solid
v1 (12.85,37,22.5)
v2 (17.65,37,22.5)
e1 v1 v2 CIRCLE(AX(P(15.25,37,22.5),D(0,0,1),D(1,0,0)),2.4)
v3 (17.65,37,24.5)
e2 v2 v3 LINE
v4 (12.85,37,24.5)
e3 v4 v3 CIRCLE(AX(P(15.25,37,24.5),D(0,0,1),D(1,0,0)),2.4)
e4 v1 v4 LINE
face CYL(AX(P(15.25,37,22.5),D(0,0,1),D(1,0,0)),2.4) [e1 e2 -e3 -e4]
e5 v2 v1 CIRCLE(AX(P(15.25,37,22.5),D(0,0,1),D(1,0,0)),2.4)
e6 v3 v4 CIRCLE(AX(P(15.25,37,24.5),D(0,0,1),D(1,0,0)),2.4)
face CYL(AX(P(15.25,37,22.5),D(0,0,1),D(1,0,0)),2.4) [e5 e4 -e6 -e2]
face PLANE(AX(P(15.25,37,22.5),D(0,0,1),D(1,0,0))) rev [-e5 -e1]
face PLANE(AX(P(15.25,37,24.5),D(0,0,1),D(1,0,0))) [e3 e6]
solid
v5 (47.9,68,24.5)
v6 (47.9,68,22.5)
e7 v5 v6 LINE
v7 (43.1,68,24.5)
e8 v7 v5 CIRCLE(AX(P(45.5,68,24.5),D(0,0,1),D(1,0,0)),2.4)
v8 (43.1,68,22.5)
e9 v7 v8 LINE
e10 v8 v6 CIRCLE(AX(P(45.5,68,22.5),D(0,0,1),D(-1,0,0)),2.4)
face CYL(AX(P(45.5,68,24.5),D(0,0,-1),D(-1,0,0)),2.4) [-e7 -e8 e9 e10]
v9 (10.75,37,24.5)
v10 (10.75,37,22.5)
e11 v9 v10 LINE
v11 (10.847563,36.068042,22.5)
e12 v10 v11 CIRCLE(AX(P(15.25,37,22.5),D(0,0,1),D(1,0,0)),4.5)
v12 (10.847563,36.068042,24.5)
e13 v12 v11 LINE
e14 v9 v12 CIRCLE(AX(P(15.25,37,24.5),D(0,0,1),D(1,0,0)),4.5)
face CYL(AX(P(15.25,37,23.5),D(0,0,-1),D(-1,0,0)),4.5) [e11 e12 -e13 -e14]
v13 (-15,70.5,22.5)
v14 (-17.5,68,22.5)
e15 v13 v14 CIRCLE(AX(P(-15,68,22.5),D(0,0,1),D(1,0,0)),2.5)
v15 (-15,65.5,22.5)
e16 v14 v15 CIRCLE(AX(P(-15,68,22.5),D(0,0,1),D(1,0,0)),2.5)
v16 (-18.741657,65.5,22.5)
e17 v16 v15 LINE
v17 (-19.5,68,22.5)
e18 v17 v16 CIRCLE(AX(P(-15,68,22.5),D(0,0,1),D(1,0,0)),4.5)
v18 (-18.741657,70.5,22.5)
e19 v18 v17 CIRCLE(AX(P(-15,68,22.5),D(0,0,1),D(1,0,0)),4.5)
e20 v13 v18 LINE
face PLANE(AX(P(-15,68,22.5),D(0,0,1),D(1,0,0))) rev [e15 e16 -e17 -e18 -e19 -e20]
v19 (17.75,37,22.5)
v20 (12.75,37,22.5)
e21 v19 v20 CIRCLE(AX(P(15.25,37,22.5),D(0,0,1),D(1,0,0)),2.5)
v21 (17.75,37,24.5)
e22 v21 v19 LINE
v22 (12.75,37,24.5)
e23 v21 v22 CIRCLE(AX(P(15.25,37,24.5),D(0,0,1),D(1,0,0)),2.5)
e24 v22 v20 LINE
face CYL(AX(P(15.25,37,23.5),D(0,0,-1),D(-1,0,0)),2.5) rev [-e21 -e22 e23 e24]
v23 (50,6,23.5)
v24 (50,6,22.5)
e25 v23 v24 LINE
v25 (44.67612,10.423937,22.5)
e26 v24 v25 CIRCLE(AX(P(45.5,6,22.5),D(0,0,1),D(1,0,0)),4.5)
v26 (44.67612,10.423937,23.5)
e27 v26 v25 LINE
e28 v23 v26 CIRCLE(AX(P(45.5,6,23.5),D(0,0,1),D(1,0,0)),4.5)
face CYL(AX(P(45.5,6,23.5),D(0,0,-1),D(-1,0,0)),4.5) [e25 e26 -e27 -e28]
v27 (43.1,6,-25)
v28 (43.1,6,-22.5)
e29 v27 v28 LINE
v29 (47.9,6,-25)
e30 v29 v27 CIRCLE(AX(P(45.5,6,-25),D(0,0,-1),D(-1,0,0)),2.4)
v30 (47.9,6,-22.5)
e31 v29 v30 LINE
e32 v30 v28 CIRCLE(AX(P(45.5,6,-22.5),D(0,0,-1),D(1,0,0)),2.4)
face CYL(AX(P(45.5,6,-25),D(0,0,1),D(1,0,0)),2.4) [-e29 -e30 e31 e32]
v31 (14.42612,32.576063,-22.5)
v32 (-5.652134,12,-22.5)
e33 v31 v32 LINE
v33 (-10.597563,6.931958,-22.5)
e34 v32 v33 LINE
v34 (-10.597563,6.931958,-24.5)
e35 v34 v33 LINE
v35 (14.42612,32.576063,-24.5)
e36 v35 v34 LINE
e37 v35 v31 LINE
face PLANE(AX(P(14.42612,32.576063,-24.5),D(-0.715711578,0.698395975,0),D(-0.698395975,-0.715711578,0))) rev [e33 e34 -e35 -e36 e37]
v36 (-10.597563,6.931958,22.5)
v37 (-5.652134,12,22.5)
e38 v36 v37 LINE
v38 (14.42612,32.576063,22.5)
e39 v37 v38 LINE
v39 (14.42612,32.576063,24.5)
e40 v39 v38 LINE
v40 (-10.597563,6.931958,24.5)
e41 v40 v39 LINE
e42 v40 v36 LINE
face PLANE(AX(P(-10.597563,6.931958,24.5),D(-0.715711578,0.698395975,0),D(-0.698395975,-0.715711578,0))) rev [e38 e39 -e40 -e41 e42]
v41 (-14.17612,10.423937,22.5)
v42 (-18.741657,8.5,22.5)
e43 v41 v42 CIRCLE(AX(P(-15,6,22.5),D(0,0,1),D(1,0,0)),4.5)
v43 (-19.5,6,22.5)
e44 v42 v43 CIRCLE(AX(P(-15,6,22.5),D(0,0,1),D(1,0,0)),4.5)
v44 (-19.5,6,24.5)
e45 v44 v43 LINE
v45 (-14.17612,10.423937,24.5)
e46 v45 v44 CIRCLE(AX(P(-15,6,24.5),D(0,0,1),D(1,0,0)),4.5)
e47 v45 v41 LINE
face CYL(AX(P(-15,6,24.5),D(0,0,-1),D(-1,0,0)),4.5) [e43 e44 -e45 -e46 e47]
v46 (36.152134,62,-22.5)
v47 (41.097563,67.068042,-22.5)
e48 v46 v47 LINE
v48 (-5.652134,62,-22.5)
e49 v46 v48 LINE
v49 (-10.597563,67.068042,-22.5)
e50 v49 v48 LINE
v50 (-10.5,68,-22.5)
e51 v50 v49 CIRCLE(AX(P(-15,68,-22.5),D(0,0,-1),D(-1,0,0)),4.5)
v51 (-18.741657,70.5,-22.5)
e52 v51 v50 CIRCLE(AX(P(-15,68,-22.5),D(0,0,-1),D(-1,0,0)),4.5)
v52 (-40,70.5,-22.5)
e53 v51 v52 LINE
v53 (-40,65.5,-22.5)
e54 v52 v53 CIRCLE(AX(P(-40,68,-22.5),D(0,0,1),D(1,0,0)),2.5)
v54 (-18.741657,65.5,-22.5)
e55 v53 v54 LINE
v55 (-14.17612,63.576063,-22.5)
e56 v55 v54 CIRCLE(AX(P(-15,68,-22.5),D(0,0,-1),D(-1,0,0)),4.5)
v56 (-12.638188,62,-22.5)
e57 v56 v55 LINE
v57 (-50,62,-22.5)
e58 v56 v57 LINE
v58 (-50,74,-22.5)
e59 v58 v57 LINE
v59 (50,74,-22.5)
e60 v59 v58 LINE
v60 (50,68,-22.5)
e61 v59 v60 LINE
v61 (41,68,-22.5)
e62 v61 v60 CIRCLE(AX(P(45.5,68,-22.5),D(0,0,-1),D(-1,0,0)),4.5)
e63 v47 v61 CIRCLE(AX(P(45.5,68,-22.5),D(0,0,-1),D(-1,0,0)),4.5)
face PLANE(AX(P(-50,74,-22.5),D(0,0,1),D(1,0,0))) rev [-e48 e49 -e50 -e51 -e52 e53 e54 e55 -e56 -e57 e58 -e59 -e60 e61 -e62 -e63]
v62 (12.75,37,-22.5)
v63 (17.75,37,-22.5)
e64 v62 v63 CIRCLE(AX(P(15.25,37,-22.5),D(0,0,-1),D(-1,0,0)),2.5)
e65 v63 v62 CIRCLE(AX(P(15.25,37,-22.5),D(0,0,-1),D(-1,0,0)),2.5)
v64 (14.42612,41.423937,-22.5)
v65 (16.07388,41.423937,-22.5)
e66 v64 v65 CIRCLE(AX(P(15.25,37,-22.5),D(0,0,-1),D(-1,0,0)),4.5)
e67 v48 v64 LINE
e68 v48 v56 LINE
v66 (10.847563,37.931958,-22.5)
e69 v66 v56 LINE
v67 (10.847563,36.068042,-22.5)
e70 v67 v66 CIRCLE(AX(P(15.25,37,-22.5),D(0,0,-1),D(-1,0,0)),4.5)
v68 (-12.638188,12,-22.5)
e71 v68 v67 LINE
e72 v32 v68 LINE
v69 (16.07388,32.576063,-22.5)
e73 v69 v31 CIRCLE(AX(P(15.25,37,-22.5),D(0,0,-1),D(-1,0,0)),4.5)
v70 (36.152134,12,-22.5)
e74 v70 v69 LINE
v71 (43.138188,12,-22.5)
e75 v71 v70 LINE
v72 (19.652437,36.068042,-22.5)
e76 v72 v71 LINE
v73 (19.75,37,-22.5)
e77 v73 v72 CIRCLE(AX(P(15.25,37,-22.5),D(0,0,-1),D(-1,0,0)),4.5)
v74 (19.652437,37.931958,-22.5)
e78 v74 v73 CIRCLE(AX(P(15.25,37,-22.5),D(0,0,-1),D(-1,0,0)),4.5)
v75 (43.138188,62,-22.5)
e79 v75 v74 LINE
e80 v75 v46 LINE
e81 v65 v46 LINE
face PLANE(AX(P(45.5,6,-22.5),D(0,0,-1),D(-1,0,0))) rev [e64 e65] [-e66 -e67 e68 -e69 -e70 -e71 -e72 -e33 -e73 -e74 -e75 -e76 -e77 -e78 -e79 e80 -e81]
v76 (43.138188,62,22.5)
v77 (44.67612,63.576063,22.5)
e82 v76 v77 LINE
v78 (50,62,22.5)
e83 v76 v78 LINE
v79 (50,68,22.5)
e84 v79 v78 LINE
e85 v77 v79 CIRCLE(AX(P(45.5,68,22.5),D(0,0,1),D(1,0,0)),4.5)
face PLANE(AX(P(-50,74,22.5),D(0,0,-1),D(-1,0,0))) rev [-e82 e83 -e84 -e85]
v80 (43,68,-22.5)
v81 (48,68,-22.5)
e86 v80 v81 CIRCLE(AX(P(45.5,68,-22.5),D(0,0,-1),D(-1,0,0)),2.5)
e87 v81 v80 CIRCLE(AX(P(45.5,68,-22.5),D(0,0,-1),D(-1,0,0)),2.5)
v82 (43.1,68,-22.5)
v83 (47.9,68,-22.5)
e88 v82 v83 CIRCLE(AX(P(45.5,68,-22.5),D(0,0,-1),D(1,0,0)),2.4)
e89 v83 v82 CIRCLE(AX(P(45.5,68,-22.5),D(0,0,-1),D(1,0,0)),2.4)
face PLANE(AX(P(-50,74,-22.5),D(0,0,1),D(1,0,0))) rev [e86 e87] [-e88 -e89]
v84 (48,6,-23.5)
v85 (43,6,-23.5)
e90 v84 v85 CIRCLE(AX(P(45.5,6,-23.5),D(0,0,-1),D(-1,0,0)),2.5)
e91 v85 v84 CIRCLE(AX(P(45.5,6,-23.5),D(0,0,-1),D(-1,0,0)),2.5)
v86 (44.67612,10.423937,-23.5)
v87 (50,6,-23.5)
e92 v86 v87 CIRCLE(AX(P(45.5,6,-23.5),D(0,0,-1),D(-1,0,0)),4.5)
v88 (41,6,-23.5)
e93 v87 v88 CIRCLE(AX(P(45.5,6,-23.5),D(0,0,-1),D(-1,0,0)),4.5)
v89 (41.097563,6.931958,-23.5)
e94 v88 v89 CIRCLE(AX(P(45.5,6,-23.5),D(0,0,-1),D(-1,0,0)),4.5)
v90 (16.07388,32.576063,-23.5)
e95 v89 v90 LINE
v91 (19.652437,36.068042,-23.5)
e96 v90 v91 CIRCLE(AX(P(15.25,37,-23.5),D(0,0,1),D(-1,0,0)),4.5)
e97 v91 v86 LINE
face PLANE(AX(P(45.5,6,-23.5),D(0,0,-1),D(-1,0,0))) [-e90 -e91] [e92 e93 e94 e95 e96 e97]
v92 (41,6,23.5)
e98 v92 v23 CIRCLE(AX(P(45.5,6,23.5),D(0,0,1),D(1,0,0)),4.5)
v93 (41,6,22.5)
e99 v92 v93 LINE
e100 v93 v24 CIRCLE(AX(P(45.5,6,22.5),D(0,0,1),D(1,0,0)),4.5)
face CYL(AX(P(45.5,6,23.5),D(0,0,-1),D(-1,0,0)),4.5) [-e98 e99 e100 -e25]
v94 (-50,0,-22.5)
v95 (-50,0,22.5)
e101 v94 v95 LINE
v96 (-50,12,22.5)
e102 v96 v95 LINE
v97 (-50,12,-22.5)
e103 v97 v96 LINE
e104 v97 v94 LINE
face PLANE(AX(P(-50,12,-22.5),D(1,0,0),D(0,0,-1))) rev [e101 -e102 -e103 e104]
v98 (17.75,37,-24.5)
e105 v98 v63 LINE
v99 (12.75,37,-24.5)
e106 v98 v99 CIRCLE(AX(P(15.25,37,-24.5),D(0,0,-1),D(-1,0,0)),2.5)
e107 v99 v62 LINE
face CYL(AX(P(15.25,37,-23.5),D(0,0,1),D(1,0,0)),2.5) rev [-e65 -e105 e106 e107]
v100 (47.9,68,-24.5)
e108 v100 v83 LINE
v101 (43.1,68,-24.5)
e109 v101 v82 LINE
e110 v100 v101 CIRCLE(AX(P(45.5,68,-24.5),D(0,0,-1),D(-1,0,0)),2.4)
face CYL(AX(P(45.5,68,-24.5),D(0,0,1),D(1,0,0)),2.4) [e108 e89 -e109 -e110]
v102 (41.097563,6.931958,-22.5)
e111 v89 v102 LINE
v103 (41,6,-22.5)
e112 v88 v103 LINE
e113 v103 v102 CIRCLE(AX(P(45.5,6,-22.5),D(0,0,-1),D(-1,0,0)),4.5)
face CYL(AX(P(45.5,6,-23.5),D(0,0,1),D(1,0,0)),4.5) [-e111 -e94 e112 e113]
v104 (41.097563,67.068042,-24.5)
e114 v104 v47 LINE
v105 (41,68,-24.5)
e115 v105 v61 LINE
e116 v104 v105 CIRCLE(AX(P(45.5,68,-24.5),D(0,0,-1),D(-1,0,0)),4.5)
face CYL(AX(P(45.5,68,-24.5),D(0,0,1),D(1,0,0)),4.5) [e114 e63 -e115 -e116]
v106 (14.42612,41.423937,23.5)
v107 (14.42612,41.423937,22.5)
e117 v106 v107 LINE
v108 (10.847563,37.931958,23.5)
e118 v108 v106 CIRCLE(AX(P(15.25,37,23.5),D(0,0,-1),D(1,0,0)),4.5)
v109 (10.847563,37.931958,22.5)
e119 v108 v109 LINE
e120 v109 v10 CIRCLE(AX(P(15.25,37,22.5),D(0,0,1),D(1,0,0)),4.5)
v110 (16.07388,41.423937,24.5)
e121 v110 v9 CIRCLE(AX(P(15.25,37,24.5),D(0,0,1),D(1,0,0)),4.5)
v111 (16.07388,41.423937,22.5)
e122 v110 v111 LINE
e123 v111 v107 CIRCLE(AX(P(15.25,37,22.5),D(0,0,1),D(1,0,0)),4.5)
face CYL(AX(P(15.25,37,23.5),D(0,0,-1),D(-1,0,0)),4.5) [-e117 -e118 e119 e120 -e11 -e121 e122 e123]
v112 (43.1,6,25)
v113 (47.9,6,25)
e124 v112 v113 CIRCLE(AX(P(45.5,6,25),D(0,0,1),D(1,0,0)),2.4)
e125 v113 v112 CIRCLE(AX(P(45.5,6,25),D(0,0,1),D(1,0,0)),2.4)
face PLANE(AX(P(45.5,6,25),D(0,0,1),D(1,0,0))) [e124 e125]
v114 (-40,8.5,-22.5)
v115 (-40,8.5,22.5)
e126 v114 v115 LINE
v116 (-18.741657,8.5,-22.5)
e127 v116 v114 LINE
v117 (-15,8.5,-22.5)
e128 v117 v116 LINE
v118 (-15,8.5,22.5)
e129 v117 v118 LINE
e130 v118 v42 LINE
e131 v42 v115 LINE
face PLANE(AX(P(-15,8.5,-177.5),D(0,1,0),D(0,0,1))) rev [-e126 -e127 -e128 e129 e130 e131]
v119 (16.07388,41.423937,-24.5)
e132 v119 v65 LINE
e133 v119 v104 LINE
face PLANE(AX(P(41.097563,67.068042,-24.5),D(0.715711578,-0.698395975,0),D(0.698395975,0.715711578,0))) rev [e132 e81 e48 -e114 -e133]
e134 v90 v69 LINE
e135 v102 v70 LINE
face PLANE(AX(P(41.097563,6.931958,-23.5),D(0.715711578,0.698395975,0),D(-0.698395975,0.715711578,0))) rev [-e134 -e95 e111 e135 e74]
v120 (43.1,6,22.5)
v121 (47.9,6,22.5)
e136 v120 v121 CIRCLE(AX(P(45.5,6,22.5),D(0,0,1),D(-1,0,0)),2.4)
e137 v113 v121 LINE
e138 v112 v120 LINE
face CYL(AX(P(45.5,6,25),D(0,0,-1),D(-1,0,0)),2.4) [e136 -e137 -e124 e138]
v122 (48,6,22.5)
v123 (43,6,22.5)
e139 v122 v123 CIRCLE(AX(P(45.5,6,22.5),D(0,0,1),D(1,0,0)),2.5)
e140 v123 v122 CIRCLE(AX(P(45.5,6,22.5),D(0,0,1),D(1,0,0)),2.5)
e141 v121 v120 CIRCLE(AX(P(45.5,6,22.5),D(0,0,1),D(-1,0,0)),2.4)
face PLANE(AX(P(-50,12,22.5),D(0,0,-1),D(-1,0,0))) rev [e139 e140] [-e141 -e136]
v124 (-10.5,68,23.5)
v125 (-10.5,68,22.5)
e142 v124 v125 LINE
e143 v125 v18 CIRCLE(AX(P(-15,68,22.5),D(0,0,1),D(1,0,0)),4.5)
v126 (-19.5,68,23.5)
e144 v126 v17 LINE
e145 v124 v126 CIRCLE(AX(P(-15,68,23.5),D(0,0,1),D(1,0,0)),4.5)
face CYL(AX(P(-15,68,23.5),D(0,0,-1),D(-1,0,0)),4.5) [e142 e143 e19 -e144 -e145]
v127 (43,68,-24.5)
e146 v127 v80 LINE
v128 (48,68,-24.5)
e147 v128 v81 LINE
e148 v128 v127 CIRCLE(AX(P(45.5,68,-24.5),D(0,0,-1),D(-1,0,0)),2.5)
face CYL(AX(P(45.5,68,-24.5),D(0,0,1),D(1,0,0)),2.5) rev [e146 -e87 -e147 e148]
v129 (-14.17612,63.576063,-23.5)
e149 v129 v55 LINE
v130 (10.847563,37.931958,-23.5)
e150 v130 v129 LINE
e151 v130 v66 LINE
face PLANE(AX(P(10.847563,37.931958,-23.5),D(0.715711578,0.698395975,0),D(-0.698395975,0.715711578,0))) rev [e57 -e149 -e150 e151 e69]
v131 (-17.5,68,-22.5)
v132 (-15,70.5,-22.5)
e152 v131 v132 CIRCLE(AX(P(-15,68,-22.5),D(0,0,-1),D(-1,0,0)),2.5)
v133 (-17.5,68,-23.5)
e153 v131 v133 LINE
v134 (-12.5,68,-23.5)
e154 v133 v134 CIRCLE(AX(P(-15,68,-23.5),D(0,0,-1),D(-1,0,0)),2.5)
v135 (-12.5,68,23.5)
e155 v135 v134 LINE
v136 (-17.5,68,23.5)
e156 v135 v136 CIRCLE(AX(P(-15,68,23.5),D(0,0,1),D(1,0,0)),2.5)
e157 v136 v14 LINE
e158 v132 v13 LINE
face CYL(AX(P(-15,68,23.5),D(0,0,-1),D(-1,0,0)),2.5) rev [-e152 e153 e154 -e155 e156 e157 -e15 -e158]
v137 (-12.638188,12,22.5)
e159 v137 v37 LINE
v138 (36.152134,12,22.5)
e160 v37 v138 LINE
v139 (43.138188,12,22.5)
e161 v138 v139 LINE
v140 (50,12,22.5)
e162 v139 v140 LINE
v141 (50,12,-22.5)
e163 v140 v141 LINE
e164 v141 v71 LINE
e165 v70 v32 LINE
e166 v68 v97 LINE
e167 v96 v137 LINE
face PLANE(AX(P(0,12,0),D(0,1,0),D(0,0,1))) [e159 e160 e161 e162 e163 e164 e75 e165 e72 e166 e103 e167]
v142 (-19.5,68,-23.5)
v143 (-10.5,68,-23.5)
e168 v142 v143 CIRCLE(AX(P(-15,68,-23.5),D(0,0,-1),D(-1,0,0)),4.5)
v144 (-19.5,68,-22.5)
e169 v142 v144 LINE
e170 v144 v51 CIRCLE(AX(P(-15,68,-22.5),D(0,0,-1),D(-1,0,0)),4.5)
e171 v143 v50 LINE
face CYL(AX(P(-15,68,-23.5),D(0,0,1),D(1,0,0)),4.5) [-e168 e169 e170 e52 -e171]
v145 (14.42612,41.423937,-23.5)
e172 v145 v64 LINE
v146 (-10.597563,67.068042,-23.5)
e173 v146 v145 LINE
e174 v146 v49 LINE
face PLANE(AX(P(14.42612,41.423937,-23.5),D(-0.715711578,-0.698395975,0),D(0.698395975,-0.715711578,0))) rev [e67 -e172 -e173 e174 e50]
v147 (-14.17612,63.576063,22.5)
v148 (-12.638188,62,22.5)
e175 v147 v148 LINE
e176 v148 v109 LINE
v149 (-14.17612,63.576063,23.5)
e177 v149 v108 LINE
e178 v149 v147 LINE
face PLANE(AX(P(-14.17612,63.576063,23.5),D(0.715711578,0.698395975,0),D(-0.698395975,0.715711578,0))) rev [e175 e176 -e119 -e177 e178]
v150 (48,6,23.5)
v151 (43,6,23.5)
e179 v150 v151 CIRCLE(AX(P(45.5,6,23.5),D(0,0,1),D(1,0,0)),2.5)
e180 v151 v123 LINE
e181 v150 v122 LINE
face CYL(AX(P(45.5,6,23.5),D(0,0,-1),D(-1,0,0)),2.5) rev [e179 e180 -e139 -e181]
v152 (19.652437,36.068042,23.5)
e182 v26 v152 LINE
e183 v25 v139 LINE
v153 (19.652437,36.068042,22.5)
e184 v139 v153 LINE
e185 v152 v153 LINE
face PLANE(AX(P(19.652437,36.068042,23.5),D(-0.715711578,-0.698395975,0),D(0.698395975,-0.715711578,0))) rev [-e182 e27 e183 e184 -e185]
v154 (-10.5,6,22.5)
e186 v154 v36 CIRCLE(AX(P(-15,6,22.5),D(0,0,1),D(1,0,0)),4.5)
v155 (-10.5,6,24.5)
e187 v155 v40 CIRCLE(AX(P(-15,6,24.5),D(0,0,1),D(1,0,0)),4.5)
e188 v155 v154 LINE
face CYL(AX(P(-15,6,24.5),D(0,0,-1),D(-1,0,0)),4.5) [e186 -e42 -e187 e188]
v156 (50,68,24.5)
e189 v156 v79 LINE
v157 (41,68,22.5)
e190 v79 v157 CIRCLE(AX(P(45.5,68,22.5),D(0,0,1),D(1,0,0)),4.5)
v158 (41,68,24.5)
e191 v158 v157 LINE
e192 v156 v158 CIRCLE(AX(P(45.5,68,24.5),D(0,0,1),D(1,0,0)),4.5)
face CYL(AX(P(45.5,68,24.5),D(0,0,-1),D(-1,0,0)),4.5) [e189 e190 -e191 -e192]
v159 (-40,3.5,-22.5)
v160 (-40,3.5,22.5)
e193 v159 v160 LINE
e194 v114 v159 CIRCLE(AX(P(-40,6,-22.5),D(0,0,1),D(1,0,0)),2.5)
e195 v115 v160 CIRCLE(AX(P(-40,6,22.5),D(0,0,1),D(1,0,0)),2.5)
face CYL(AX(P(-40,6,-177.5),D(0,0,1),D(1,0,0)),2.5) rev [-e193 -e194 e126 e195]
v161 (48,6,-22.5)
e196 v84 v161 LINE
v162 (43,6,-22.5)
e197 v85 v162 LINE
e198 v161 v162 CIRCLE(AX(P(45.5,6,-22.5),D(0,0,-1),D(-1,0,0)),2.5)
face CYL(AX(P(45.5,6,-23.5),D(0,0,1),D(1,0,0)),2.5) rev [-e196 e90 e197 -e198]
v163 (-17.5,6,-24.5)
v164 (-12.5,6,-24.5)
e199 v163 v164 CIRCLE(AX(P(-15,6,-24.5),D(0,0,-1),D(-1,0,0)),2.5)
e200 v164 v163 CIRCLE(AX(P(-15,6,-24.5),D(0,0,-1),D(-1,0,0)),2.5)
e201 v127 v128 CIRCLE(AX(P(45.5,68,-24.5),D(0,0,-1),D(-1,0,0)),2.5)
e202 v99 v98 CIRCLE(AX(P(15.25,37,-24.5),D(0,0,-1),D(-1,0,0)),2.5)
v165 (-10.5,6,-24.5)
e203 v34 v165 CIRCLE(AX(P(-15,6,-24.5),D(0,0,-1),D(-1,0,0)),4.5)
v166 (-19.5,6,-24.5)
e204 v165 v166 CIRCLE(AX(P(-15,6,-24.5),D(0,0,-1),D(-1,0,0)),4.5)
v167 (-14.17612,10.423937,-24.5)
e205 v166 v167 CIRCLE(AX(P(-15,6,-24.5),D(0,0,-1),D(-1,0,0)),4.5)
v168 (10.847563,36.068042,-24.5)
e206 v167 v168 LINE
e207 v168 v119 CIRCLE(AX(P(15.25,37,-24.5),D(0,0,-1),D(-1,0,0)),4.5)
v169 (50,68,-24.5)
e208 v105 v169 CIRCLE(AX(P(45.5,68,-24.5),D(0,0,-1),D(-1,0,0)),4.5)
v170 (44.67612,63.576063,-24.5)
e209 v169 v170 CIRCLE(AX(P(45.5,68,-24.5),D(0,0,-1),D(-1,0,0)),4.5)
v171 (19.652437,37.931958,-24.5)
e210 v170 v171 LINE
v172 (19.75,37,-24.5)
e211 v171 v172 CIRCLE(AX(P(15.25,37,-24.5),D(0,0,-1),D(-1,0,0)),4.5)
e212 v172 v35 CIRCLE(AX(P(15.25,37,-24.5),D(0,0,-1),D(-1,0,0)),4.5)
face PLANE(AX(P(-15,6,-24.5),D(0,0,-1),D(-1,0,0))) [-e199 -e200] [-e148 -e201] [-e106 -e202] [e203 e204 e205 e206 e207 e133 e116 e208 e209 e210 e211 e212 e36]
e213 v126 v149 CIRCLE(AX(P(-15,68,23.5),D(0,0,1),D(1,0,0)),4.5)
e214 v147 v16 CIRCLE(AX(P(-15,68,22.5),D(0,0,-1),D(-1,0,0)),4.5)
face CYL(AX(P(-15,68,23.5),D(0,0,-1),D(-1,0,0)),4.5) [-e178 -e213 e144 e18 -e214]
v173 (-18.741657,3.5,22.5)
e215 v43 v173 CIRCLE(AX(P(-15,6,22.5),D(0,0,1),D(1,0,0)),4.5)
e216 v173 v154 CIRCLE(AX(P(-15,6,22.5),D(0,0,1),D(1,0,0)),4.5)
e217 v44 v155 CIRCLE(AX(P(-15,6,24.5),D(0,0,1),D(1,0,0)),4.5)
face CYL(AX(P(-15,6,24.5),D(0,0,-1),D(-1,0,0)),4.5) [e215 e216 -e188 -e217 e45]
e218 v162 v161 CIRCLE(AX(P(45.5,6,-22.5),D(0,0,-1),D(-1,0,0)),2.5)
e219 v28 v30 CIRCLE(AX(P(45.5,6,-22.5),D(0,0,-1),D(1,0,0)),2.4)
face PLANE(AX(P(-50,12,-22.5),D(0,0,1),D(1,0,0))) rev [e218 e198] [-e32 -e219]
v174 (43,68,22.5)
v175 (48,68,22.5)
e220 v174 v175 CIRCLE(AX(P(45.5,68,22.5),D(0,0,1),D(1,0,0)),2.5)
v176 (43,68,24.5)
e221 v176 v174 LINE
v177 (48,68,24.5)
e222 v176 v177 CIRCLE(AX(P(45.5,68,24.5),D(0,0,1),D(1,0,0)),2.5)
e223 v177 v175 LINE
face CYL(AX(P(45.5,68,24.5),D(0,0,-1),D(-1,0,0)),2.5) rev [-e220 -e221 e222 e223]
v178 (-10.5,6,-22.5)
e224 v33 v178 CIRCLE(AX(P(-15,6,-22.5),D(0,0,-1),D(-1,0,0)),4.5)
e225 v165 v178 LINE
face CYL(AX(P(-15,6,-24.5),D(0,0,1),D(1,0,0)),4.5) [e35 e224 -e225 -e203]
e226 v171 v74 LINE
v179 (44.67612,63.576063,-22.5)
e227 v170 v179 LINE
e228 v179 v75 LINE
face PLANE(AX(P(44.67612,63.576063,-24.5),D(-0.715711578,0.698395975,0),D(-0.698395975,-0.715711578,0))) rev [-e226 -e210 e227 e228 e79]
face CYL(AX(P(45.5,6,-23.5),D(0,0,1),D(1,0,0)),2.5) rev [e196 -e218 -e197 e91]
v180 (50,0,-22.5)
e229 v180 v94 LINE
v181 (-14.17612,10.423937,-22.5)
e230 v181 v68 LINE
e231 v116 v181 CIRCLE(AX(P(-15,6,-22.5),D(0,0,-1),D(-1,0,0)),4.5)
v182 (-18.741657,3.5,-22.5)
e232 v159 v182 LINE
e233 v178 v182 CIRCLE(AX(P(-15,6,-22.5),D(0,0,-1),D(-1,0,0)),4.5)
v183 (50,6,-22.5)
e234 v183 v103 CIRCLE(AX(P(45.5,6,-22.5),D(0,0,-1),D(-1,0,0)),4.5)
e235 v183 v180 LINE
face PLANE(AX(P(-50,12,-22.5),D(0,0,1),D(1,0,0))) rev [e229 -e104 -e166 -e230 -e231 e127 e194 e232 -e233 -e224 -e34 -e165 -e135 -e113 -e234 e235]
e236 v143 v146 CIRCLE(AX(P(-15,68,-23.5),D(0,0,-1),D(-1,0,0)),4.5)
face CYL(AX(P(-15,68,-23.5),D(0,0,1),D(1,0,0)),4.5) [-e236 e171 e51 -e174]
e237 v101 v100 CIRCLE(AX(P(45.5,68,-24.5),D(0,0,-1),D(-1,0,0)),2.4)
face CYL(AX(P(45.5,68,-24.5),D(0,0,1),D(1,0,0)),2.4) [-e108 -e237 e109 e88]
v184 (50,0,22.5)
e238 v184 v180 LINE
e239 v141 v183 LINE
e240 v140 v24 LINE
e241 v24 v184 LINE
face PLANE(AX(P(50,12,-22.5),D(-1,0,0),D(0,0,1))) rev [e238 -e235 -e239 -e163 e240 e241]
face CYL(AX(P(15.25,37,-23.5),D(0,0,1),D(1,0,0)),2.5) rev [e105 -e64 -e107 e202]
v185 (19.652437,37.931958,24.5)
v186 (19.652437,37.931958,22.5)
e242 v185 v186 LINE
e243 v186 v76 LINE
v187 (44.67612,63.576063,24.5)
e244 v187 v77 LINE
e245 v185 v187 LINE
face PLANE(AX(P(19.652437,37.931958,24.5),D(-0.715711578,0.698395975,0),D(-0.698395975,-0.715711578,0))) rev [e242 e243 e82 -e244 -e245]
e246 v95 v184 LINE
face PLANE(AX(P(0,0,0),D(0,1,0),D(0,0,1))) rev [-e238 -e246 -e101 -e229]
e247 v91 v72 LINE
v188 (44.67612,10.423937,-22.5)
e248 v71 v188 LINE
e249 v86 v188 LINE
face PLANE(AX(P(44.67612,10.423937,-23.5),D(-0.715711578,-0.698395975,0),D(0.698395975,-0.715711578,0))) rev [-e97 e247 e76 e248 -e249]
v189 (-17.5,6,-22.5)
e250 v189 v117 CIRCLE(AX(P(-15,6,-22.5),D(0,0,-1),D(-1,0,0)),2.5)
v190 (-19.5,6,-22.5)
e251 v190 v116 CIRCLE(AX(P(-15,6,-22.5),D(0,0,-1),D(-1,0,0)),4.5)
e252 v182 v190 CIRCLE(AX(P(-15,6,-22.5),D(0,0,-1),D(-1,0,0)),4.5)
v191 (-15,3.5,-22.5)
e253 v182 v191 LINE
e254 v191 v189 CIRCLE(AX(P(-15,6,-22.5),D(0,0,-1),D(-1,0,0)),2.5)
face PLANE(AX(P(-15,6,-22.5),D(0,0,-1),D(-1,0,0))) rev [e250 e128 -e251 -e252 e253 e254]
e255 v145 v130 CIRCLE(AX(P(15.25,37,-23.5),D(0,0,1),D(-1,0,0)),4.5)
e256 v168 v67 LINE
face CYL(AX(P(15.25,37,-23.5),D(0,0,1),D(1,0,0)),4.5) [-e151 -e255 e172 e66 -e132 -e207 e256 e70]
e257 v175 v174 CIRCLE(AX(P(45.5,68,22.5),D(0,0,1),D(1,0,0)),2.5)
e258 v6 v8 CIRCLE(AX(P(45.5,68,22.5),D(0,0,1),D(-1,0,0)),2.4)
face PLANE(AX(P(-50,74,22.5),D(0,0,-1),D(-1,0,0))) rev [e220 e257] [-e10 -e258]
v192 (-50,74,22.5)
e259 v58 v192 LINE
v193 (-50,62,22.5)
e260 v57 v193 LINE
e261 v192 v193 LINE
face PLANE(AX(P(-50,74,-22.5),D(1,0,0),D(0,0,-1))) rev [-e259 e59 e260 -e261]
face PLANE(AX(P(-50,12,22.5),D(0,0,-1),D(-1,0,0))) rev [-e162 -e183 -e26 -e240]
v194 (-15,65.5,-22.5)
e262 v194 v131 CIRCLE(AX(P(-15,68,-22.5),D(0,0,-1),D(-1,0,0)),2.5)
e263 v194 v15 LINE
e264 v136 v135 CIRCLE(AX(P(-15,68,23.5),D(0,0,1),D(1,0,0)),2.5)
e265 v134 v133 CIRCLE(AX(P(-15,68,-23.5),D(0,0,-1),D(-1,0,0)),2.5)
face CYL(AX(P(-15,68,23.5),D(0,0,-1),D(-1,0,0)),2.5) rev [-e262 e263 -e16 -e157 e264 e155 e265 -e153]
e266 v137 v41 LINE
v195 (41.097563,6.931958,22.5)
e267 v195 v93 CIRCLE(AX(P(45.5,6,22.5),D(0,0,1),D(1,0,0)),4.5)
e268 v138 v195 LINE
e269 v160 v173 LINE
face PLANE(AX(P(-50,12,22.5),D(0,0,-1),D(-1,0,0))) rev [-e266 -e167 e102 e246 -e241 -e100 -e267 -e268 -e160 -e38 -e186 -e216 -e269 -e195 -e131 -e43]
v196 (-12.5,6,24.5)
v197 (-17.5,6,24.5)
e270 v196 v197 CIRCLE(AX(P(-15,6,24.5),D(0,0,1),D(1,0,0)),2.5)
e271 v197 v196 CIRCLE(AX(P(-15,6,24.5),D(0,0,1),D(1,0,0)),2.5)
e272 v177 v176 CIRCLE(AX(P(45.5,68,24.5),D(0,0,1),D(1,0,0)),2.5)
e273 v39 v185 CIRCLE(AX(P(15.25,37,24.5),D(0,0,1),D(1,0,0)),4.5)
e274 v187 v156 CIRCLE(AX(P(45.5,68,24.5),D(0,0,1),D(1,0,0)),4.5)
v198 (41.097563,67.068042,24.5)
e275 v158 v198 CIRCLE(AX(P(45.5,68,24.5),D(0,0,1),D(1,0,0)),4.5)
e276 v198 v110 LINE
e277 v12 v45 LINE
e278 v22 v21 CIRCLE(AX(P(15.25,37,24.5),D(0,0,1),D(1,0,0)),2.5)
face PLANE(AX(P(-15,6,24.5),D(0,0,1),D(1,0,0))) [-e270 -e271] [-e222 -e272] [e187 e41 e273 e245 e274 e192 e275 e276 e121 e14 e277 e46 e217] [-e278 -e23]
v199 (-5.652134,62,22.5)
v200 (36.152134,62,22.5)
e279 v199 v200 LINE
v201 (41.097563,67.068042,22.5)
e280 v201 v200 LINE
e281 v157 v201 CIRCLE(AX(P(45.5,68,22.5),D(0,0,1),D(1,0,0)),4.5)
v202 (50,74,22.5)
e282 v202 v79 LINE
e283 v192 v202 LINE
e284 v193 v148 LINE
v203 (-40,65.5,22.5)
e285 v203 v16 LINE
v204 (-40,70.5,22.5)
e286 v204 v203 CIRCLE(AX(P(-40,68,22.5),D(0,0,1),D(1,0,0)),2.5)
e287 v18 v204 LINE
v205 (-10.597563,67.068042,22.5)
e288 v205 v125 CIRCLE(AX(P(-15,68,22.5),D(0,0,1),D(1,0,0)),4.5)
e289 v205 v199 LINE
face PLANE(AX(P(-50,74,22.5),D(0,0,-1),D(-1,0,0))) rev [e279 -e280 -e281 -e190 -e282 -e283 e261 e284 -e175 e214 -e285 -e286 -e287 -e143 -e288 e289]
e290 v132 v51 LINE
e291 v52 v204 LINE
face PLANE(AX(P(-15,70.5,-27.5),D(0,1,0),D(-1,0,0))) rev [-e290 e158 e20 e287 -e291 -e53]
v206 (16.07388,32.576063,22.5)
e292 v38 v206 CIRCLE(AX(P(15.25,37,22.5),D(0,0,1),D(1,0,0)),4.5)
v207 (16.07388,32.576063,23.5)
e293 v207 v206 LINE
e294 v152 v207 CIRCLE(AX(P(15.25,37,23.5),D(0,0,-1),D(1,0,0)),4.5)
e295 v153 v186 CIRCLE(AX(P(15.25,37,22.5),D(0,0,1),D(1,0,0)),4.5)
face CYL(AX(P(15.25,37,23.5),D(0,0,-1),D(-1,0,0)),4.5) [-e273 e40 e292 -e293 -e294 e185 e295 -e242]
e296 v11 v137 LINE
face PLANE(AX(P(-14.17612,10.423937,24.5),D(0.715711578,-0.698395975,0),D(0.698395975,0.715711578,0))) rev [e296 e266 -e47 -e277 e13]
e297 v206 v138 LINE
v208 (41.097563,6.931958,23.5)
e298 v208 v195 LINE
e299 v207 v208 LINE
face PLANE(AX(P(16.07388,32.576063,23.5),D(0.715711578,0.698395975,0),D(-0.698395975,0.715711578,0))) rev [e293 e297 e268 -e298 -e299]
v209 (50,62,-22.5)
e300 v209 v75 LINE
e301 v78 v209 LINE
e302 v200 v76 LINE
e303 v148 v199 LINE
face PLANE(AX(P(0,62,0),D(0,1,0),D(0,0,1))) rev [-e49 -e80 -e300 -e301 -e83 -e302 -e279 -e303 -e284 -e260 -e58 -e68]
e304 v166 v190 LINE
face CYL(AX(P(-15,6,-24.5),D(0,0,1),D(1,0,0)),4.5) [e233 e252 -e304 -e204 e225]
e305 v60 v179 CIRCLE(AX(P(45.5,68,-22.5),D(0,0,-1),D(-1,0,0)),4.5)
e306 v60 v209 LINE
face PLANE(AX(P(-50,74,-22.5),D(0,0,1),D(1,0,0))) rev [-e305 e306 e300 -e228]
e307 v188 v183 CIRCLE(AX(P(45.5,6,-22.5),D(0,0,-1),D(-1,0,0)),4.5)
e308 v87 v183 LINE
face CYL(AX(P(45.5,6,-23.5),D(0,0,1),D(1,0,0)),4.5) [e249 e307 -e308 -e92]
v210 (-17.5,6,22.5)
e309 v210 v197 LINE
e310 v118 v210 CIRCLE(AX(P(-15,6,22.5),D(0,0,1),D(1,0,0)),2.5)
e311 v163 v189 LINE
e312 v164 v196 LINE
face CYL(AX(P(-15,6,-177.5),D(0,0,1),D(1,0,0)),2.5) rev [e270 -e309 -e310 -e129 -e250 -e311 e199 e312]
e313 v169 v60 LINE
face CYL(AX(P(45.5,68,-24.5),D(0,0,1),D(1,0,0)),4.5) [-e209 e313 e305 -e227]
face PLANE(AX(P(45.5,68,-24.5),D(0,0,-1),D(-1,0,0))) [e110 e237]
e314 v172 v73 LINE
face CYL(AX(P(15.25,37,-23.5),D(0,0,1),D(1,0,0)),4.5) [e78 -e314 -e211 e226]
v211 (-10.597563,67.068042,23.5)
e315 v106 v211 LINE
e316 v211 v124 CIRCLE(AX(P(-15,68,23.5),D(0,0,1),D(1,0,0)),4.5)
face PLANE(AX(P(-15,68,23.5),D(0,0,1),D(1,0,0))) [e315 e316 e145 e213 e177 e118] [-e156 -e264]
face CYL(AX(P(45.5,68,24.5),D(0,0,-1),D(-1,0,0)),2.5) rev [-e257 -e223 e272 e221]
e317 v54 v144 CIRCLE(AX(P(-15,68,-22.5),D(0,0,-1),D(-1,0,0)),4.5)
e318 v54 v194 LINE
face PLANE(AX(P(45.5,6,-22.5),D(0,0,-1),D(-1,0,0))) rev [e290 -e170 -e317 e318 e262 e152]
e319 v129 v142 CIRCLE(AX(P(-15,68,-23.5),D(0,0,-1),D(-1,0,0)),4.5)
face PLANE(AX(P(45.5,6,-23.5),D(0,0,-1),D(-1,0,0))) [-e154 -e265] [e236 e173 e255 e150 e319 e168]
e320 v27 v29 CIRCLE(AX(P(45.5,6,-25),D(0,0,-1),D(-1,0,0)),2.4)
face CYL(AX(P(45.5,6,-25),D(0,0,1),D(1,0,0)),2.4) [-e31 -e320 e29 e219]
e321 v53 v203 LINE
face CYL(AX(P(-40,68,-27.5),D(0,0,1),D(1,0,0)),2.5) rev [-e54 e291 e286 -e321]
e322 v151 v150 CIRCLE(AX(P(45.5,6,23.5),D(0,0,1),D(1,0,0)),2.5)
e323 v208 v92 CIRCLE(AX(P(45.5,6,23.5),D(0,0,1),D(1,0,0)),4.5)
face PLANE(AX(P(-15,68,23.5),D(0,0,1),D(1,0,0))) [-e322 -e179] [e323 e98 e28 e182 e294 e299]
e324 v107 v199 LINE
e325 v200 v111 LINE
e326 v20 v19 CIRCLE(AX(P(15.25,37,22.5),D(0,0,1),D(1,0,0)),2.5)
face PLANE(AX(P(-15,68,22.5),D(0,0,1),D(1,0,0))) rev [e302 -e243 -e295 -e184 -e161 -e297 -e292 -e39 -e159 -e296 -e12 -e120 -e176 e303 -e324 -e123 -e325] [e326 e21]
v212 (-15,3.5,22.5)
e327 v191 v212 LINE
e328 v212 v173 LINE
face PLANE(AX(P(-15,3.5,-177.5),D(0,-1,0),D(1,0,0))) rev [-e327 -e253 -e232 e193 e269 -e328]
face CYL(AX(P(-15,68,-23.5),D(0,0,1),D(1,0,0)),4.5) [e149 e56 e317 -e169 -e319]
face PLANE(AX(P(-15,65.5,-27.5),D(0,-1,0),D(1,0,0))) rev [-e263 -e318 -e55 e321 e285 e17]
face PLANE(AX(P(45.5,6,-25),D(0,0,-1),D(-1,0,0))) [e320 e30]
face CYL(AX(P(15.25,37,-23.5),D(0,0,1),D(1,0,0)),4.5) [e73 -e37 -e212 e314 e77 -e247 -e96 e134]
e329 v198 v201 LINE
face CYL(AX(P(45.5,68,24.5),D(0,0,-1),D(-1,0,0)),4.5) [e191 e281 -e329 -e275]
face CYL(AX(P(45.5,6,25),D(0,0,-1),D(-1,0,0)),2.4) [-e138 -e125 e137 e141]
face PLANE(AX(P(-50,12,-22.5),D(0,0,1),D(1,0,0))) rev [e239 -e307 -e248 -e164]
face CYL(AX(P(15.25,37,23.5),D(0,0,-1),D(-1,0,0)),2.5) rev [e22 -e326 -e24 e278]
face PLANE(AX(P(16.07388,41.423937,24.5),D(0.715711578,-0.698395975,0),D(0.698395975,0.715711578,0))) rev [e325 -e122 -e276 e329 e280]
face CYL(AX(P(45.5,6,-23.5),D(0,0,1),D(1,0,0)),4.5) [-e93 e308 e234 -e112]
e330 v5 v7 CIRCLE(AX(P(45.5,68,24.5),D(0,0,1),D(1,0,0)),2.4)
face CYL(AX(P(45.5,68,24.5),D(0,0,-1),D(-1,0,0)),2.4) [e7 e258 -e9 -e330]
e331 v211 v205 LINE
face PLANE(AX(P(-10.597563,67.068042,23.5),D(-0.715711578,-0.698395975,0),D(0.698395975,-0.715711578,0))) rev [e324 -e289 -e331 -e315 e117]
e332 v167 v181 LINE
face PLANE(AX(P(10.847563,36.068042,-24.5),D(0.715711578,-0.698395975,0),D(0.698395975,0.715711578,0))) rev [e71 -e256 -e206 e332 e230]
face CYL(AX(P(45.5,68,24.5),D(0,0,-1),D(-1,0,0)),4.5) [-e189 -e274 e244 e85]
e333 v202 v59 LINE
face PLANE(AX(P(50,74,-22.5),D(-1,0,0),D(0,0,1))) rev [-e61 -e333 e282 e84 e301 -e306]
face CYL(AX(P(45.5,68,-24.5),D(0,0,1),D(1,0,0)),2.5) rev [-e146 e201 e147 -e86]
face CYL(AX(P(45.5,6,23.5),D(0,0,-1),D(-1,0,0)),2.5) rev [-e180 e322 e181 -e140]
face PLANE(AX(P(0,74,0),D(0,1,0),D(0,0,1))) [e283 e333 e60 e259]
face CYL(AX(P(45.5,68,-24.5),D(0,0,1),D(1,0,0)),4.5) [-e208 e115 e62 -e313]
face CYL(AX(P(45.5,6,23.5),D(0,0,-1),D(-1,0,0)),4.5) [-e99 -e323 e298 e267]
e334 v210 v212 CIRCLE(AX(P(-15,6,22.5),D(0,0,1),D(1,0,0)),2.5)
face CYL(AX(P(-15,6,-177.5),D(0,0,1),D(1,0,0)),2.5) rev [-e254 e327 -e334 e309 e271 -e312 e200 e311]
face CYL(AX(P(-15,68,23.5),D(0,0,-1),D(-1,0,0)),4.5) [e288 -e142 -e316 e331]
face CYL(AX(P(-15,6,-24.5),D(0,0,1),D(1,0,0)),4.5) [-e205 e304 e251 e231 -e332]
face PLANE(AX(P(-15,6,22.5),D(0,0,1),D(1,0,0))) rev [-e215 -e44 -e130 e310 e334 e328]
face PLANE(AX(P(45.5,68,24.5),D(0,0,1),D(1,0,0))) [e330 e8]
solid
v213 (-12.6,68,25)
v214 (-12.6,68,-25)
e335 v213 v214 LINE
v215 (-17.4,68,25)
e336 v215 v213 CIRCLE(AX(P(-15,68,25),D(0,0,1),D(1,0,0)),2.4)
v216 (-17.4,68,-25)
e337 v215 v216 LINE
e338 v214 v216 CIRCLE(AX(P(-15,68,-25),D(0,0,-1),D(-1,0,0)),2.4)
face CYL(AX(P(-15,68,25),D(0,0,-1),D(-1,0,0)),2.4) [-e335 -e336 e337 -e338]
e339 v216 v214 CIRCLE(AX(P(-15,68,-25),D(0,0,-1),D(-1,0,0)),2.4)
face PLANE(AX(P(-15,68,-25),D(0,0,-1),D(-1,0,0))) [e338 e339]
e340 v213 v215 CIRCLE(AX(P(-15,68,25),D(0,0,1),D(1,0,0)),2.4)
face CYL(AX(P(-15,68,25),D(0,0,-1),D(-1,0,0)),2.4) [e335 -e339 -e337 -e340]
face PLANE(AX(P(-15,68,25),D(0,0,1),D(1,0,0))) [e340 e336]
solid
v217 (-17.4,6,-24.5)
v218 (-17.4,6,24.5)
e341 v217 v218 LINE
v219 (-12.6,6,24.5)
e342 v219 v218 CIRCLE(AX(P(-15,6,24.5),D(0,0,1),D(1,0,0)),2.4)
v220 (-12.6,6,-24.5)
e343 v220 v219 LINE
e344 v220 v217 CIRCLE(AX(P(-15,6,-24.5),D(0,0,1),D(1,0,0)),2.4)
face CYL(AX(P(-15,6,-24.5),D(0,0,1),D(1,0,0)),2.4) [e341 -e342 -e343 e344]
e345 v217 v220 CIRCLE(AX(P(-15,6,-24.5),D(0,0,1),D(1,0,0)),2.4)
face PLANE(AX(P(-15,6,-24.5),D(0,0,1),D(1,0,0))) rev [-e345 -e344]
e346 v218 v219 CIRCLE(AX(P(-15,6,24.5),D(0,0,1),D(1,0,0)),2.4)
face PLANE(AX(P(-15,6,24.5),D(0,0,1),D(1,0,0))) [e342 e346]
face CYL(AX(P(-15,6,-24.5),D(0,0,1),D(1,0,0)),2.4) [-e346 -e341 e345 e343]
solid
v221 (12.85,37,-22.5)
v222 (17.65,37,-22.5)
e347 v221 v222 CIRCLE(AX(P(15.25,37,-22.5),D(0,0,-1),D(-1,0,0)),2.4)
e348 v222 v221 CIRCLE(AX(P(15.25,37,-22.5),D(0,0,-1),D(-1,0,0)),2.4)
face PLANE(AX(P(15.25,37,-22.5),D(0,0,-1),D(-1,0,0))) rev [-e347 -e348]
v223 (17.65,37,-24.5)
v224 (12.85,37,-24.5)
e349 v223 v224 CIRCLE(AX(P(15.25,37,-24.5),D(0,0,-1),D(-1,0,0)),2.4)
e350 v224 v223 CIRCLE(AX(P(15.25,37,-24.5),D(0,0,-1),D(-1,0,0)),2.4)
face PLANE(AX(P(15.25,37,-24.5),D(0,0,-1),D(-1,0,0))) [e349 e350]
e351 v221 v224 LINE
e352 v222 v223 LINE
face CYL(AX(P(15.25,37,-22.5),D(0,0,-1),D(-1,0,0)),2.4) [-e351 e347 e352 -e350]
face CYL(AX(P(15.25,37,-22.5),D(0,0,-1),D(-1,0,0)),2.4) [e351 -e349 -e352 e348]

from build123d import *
from build123d.topology import SkipClean

# Parameters (mm, degrees)
BASE_PLATE_SKETCH_W              = 100
BASE_PLATE_SKETCH_H              = 45
BASE_PLATE_DEPTH                 = 12
BASE_PLATE_GUIDE_SLOT_DEPTH      = 200
TOP_PLATE_SKETCH_W               = 100
TOP_PLATE_SKETCH_H               = 45
TOP_PLATE_DEPTH                  = 12
TOP_PLATE_GUIDE_SLOT_DEPTH       = 50
FRONT_SCISSOR_ARM_A_SKETCH_R     = 2.5
FRONT_SCISSOR_ARM_A_DEPTH        = 1
FRONT_SCISSOR_ARM_B_SKETCH_R     = 2.5
FRONT_SCISSOR_ARM_B_DEPTH        = 2
FRONT_START                      = -2
FRONT_ARM_LINK_PIN_SKETCH_R      = 4.5
FRONT_ARM_LINK_PIN_SKETCH_R_2    = 2.5
FRONT_ARM_LINK_PIN_DEPTH         = 2
CENTER_PIVOT_PIN_FRONT_SKETCH_R  = 2.4
CENTER_PIVOT_PIN_FRONT_4_8_DEPTH = 2
LOWER_CROSS_PIN_SKETCH_R         = 2.4
LOWER_CROSS_PIN_4_8X49_DEPTH     = 49
UPPER_CROSS_PIN_HEAD_SKETCH_R    = 2.4
UPPER_CROSS_PIN_HEAD_DEPTH       = 1.5
UPPER_CROSS_PIN_SKETCH_R         = 2.4
UPPER_CROSS_PIN_4_8X47_5_DEPTH   = 47.5
FRONT_ARM_PIN_SKETCH_R           = 2.4
FRONT_ARM_PIN_4_8_DEPTH          = 2
LOWER_ROLLER_PIN_SKETCH_R        = 2.4
LOWER_ROLLER_PIN_4_8_DEPTH       = 2.5
REAR_START                       = 1
REAR_SCISSOR_ARM_A_SKETCH_R      = 2.5
REAR_SCISSOR_ARM_A_DEPTH         = 1
UPPER_START                      = 2.5
UPPER_CROSS_PIN_END_SKETCH_R     = 2.4
UPPER_CROSS_PIN_END_4_8_DEPTH    = 2.5
REAR_START_2                     = 2
REAR_SCISSOR_ARM_B_SKETCH_R      = 2.5
REAR_SCISSOR_ARM_B_DEPTH         = 2
CENTER_PIVOT_PIN_REAR_SKETCH_R   = 2.4
CENTER_PIVOT_PIN_REAR_4_8_DEPTH  = 2
REAR_ARM_PIN_SKETCH_R            = 2.4
REAR_ARM_PIN_4_8_DEPTH           = 2


with BuildPart() as part:
    # Base Plate Sketch → Base Plate (new body)
    with BuildSketch(Plane(origin=(0, 0, 0), x_dir=(1, 0, 0), z_dir=(0, 1, 0))):
        Rectangle(BASE_PLATE_SKETCH_W, BASE_PLATE_SKETCH_H)
    extrude(amount=BASE_PLATE_DEPTH)

    # Base Plate Guide Slot Sketch → Base Plate Guide Slot (cut)
    with BuildSketch(Plane.XY.offset(22.5)):
        with BuildLine():
            Line((-15, 3.5), (-40, 3.5))
            ThreePointArc((-40, 3.5), (-42.5, 6), (-40, 8.5))
            Line((-40, 8.5), (-15, 8.5))
            ThreePointArc((-15, 8.5), (-12.5, 6), (-15, 3.5))
        make_face()
    extrude(amount=-BASE_PLATE_GUIDE_SLOT_DEPTH, mode=Mode.SUBTRACT)



with BuildPart() as body_2:
    # Top Plate Sketch → Top Plate (new body)
    with BuildSketch(Plane(origin=(0, 62, 0), x_dir=(1, 0, 0), z_dir=(0, 1, 0))):
        Rectangle(TOP_PLATE_SKETCH_W, TOP_PLATE_SKETCH_H)
    extrude(amount=TOP_PLATE_DEPTH)

    # Top Plate Guide Slot Sketch → Top Plate Guide Slot (cut)
    with BuildSketch(Plane.XY.offset(22.5)):
        with BuildLine():
            Line((-15, 65.5), (-40, 65.5))
            ThreePointArc((-40, 65.5), (-42.5, 68), (-40, 70.5))
            Line((-40, 70.5), (-15, 70.5))
            ThreePointArc((-15, 70.5), (-12.5, 68), (-15, 65.5))
        make_face()
    extrude(amount=-TOP_PLATE_GUIDE_SLOT_DEPTH, mode=Mode.SUBTRACT)


with BuildPart() as part_1:
    with SkipClean():  # the faces are left unmerged after this step: merging them gives an invalid solid
        add(part.part)

        add(body_2.part)  # Front Scissor Arm A merges body 2
        # Front Scissor Arm A Sketch → Front Scissor Arm A (add)
        with BuildSketch(Plane.XY.offset(22.5)):
            with BuildLine():
                Line((-14.176120486, 63.576062552), (10.847562598, 37.931957574))
                ThreePointArc((10.847562598, 37.931957574), (12.029297901, 33.857218113), (16.073879514, 32.576062552))
                Line((16.073879514, 32.576062552), (41.097562598, 6.931957574))
                ThreePointArc((41.097562598, 6.931957574), (48.642781887, 2.779297901), (44.676120486, 10.423937448))
                Line((44.676120486, 10.423937448), (19.652437402, 36.068042426))
                ThreePointArc((19.652437402, 36.068042426), (18.470702099, 40.142781887), (14.426120486, 41.423937448))
                Line((14.426120486, 41.423937448), (-10.597562598, 67.068042426))
                ThreePointArc((-10.597562598, 67.068042426), (-18.142781887, 71.220702099), (-14.176120486, 63.576062552))
            make_face()
            with Locations(Location((-15, 68, 0), (0, 0, 270))):
                Circle(FRONT_SCISSOR_ARM_A_SKETCH_R, mode=Mode.SUBTRACT)
            with Locations((45.5, 6)):
                Circle(FRONT_SCISSOR_ARM_A_SKETCH_R, mode=Mode.SUBTRACT)
            with Locations((15.25, 37)):
                Circle(FRONT_SCISSOR_ARM_A_SKETCH_R, mode=Mode.SUBTRACT)
        extrude(amount=FRONT_SCISSOR_ARM_A_DEPTH)

    # Front Scissor Arm B Sketch → Front Scissor Arm B (add)
    with SkipClean():  # the faces are left unmerged after this step: merging them gives an invalid solid
        with BuildSketch(Plane.XY.offset(22.5)):
            with BuildLine():
                Line((16.073879514, 41.423937448), (41.097562598, 67.068042426))
                ThreePointArc((41.097562598, 67.068042426), (48.642781887, 71.220702099), (44.676120486, 63.576062552))
                Line((44.676120486, 63.576062552), (19.652437402, 37.931957574))
                ThreePointArc((19.652437402, 37.931957574), (18.470702099, 33.857218113), (14.426120486, 32.576062552))
                Line((14.426120486, 32.576062552), (-10.597562598, 6.931957574))
                ThreePointArc((-10.597562598, 6.931957574), (-18.142781887, 2.779297901), (-14.176120486, 10.423937448))
                Line((-14.176120486, 10.423937448), (10.847562598, 36.068042426))
                ThreePointArc((10.847562598, 36.068042426), (12.029297901, 40.142781887), (16.073879514, 41.423937448))
            make_face()
            with Locations((-15, 6)):
                Circle(FRONT_SCISSOR_ARM_B_SKETCH_R, mode=Mode.SUBTRACT)
            with Locations((45.5, 68)):
                Circle(FRONT_SCISSOR_ARM_B_SKETCH_R, mode=Mode.SUBTRACT)
            with Locations((15.25, 37)):
                Circle(FRONT_SCISSOR_ARM_B_SKETCH_R, mode=Mode.SUBTRACT)
        extrude(amount=FRONT_SCISSOR_ARM_B_DEPTH)

    # Front Arm Link Pin Sketch → Front Arm Link Pin (add)
    with SkipClean():  # the faces are left unmerged after this step: merging them gives an invalid solid
        with BuildSketch(Plane.XY.offset(24.5).offset(FRONT_START)):
            with Locations((15.25, 37)):
                Circle(FRONT_ARM_LINK_PIN_SKETCH_R)
            with Locations((15.25, 37)):
                Circle(FRONT_ARM_LINK_PIN_SKETCH_R_2, mode=Mode.SUBTRACT)
        extrude(amount=FRONT_ARM_LINK_PIN_DEPTH)

    # Front Arm Pin Sketch → Front Arm Pin Ø4.8 (add)
    with SkipClean():  # the faces are left unmerged after this step: merging them gives an invalid solid
        with BuildSketch(Plane.XY.offset(22.5)):
            with Locations(Location((45.5, 68, 0), (0, 0, 180))):
                Circle(FRONT_ARM_PIN_SKETCH_R)
        extrude(amount=FRONT_ARM_PIN_4_8_DEPTH)

    # Lower Roller Pin Sketch → Lower Roller Pin Ø4.8 (add)
    with SkipClean():  # the faces are left unmerged after this step: merging them gives an invalid solid
        with BuildSketch(Plane.XY.offset(22.5)):
            with Locations(Location((45.5, 6, 0), (0, 0, 180))):
                Circle(LOWER_ROLLER_PIN_SKETCH_R)
        extrude(amount=LOWER_ROLLER_PIN_4_8_DEPTH)

    # Rear Scissor Arm A Sketch → Rear Scissor Arm A (add)
    with BuildSketch(Plane(origin=(0, 0, -22.5), x_dir=(-1, 0, 0), z_dir=(0, 0, -1)).offset(REAR_START)):
        with BuildLine():
            Line((-14.426120486, 41.423937448), (10.597562598, 67.068042426))
            ThreePointArc((10.597562598, 67.068042426), (18.142781887, 71.220702099), (14.176120486, 63.576062552))
            Line((14.176120486, 63.576062552), (-10.847562598, 37.931957574))
            ThreePointArc((-10.847562598, 37.931957574), (-12.029297901, 33.857218113), (-16.073879514, 32.576062552))
            Line((-16.073879514, 32.576062552), (-41.097562598, 6.931957574))
            ThreePointArc((-41.097562598, 6.931957574), (-48.642781887, 2.779297901), (-44.676120486, 10.423937448))
            Line((-44.676120486, 10.423937448), (-19.652437402, 36.068042426))
            ThreePointArc((-19.652437402, 36.068042426), (-18.470702099, 40.142781887), (-14.426120486, 41.423937448))
        make_face()
        with Locations((15, 68)):
            Circle(REAR_SCISSOR_ARM_A_SKETCH_R, mode=Mode.SUBTRACT)
        with Locations(Location((-45.5, 6, 0), (0, 0, 180))):
            Circle(REAR_SCISSOR_ARM_A_SKETCH_R, mode=Mode.SUBTRACT)
        with Locations(Location((-15.25, 37, 0), (0, 0, 180))):
            Circle(REAR_SCISSOR_ARM_A_SKETCH_R, mode=Mode.SUBTRACT)
    extrude(amount=-REAR_SCISSOR_ARM_A_DEPTH)



with BuildPart() as body_2_2:
    # Center Pivot Pin Front Sketch → Center Pivot Pin Front Ø4.8 (new body)
    with BuildSketch(Plane.XY.offset(24.5)):
        with Locations((15.25, 37)):
            Circle(CENTER_PIVOT_PIN_FRONT_SKETCH_R)
    extrude(amount=-CENTER_PIVOT_PIN_FRONT_4_8_DEPTH)


with BuildPart() as body_3:
    # Lower Cross Pin Sketch → Lower Cross Pin Ø4.8x49 (new body)
    with BuildSketch(Plane.XY.offset(24.5)):
        with Locations((-15, 6)):
            Circle(LOWER_CROSS_PIN_SKETCH_R)
    extrude(amount=-LOWER_CROSS_PIN_4_8X49_DEPTH)


with BuildPart() as body_4:
    # Upper Cross Pin Head Sketch → Upper Cross Pin Head (new body)
    with BuildSketch(Plane.XY.offset(23.5)):
        with Locations((-15, 68)):
            Circle(UPPER_CROSS_PIN_HEAD_SKETCH_R)
    extrude(amount=UPPER_CROSS_PIN_HEAD_DEPTH)

    # Upper Cross Pin Sketch → Upper Cross Pin Ø4.8x47.5 (add)
    with BuildSketch(Plane.XY.offset(25)):
        with Locations((-15, 68)):
            Circle(UPPER_CROSS_PIN_SKETCH_R)
    extrude(amount=-UPPER_CROSS_PIN_4_8X47_5_DEPTH)


with BuildPart() as part_2:
    add(part_1.part)

    add(body_4.part)  # Upper Cross Pin End Ø4.8 merges body 4
    # Upper Cross Pin End Sketch → Upper Cross Pin End Ø4.8 (add)
    with BuildSketch(Plane(origin=(0, 0, -22.5), x_dir=(-1, 0, 0), z_dir=(0, 0, -1)).offset(UPPER_START)):
        with Locations((15, 68)):
            Circle(UPPER_CROSS_PIN_END_SKETCH_R)
        with Locations((-45.5, 6)):
            Circle(UPPER_CROSS_PIN_END_SKETCH_R)
    extrude(amount=-UPPER_CROSS_PIN_END_4_8_DEPTH)

    # Rear Scissor Arm B Sketch → Rear Scissor Arm B (add)
    with SkipClean():  # the faces are left unmerged after this step: merging them gives an invalid solid
        with BuildSketch(Plane(origin=(0, 0, -22.5), x_dir=(-1, 0, 0), z_dir=(0, 0, -1)).offset(REAR_START_2)):
            with BuildLine():
                Line((-10.847562598, 36.068042426), (14.176120486, 10.423937448))
                ThreePointArc((14.176120486, 10.423937448), (18.142781887, 2.779297901), (10.597562598, 6.931957574))
                Line((10.597562598, 6.931957574), (-14.426120486, 32.576062552))
                ThreePointArc((-14.426120486, 32.576062552), (-18.470702099, 33.857218113), (-19.652437402, 37.931957574))
                Line((-19.652437402, 37.931957574), (-44.676120486, 63.576062552))
                ThreePointArc((-44.676120486, 63.576062552), (-48.642781887, 71.220702099), (-41.097562598, 67.068042426))
                Line((-41.097562598, 67.068042426), (-16.073879514, 41.423937448))
                ThreePointArc((-16.073879514, 41.423937448), (-12.029297901, 40.142781887), (-10.847562598, 36.068042426))
            make_face()
            with Locations(Location((-45.5, 68, 0), (0, 0, 180))):
                Circle(REAR_SCISSOR_ARM_B_SKETCH_R, mode=Mode.SUBTRACT)
            with Locations(Location((15, 6, 0), (0, 0, 180))):
                Circle(REAR_SCISSOR_ARM_B_SKETCH_R, mode=Mode.SUBTRACT)
            with Locations(Location((-15.25, 37, 0), (0, 0, 180))):
                Circle(REAR_SCISSOR_ARM_B_SKETCH_R, mode=Mode.SUBTRACT)
        extrude(amount=-REAR_SCISSOR_ARM_B_DEPTH)

    # Rear Arm Pin Sketch → Rear Arm Pin Ø4.8 (add)
    with SkipClean():  # the faces are left unmerged after this step: merging them gives an invalid solid
        with BuildSketch(Plane(origin=(0, 0, -22.5), x_dir=(-1, 0, 0), z_dir=(0, 0, -1)).offset(REAR_START_2)):
            with Locations((-45.5, 68)):
                Circle(REAR_ARM_PIN_SKETCH_R)
        extrude(amount=-REAR_ARM_PIN_4_8_DEPTH)


with BuildPart() as body_4_2:
    # Center Pivot Pin Rear Sketch → Center Pivot Pin Rear Ø4.8 (new body)
    with BuildSketch(Plane(origin=(0, 0, -24.5), x_dir=(-1, 0, 0), z_dir=(0, 0, -1))):
        with Locations((-15.25, 37)):
            Circle(CENTER_PIVOT_PIN_REAR_SKETCH_R)
    extrude(amount=-CENTER_PIVOT_PIN_REAR_4_8_DEPTH)


solid = Compound([body_2_2.part, body_3.part, part_2.part, body_4_2.part])
